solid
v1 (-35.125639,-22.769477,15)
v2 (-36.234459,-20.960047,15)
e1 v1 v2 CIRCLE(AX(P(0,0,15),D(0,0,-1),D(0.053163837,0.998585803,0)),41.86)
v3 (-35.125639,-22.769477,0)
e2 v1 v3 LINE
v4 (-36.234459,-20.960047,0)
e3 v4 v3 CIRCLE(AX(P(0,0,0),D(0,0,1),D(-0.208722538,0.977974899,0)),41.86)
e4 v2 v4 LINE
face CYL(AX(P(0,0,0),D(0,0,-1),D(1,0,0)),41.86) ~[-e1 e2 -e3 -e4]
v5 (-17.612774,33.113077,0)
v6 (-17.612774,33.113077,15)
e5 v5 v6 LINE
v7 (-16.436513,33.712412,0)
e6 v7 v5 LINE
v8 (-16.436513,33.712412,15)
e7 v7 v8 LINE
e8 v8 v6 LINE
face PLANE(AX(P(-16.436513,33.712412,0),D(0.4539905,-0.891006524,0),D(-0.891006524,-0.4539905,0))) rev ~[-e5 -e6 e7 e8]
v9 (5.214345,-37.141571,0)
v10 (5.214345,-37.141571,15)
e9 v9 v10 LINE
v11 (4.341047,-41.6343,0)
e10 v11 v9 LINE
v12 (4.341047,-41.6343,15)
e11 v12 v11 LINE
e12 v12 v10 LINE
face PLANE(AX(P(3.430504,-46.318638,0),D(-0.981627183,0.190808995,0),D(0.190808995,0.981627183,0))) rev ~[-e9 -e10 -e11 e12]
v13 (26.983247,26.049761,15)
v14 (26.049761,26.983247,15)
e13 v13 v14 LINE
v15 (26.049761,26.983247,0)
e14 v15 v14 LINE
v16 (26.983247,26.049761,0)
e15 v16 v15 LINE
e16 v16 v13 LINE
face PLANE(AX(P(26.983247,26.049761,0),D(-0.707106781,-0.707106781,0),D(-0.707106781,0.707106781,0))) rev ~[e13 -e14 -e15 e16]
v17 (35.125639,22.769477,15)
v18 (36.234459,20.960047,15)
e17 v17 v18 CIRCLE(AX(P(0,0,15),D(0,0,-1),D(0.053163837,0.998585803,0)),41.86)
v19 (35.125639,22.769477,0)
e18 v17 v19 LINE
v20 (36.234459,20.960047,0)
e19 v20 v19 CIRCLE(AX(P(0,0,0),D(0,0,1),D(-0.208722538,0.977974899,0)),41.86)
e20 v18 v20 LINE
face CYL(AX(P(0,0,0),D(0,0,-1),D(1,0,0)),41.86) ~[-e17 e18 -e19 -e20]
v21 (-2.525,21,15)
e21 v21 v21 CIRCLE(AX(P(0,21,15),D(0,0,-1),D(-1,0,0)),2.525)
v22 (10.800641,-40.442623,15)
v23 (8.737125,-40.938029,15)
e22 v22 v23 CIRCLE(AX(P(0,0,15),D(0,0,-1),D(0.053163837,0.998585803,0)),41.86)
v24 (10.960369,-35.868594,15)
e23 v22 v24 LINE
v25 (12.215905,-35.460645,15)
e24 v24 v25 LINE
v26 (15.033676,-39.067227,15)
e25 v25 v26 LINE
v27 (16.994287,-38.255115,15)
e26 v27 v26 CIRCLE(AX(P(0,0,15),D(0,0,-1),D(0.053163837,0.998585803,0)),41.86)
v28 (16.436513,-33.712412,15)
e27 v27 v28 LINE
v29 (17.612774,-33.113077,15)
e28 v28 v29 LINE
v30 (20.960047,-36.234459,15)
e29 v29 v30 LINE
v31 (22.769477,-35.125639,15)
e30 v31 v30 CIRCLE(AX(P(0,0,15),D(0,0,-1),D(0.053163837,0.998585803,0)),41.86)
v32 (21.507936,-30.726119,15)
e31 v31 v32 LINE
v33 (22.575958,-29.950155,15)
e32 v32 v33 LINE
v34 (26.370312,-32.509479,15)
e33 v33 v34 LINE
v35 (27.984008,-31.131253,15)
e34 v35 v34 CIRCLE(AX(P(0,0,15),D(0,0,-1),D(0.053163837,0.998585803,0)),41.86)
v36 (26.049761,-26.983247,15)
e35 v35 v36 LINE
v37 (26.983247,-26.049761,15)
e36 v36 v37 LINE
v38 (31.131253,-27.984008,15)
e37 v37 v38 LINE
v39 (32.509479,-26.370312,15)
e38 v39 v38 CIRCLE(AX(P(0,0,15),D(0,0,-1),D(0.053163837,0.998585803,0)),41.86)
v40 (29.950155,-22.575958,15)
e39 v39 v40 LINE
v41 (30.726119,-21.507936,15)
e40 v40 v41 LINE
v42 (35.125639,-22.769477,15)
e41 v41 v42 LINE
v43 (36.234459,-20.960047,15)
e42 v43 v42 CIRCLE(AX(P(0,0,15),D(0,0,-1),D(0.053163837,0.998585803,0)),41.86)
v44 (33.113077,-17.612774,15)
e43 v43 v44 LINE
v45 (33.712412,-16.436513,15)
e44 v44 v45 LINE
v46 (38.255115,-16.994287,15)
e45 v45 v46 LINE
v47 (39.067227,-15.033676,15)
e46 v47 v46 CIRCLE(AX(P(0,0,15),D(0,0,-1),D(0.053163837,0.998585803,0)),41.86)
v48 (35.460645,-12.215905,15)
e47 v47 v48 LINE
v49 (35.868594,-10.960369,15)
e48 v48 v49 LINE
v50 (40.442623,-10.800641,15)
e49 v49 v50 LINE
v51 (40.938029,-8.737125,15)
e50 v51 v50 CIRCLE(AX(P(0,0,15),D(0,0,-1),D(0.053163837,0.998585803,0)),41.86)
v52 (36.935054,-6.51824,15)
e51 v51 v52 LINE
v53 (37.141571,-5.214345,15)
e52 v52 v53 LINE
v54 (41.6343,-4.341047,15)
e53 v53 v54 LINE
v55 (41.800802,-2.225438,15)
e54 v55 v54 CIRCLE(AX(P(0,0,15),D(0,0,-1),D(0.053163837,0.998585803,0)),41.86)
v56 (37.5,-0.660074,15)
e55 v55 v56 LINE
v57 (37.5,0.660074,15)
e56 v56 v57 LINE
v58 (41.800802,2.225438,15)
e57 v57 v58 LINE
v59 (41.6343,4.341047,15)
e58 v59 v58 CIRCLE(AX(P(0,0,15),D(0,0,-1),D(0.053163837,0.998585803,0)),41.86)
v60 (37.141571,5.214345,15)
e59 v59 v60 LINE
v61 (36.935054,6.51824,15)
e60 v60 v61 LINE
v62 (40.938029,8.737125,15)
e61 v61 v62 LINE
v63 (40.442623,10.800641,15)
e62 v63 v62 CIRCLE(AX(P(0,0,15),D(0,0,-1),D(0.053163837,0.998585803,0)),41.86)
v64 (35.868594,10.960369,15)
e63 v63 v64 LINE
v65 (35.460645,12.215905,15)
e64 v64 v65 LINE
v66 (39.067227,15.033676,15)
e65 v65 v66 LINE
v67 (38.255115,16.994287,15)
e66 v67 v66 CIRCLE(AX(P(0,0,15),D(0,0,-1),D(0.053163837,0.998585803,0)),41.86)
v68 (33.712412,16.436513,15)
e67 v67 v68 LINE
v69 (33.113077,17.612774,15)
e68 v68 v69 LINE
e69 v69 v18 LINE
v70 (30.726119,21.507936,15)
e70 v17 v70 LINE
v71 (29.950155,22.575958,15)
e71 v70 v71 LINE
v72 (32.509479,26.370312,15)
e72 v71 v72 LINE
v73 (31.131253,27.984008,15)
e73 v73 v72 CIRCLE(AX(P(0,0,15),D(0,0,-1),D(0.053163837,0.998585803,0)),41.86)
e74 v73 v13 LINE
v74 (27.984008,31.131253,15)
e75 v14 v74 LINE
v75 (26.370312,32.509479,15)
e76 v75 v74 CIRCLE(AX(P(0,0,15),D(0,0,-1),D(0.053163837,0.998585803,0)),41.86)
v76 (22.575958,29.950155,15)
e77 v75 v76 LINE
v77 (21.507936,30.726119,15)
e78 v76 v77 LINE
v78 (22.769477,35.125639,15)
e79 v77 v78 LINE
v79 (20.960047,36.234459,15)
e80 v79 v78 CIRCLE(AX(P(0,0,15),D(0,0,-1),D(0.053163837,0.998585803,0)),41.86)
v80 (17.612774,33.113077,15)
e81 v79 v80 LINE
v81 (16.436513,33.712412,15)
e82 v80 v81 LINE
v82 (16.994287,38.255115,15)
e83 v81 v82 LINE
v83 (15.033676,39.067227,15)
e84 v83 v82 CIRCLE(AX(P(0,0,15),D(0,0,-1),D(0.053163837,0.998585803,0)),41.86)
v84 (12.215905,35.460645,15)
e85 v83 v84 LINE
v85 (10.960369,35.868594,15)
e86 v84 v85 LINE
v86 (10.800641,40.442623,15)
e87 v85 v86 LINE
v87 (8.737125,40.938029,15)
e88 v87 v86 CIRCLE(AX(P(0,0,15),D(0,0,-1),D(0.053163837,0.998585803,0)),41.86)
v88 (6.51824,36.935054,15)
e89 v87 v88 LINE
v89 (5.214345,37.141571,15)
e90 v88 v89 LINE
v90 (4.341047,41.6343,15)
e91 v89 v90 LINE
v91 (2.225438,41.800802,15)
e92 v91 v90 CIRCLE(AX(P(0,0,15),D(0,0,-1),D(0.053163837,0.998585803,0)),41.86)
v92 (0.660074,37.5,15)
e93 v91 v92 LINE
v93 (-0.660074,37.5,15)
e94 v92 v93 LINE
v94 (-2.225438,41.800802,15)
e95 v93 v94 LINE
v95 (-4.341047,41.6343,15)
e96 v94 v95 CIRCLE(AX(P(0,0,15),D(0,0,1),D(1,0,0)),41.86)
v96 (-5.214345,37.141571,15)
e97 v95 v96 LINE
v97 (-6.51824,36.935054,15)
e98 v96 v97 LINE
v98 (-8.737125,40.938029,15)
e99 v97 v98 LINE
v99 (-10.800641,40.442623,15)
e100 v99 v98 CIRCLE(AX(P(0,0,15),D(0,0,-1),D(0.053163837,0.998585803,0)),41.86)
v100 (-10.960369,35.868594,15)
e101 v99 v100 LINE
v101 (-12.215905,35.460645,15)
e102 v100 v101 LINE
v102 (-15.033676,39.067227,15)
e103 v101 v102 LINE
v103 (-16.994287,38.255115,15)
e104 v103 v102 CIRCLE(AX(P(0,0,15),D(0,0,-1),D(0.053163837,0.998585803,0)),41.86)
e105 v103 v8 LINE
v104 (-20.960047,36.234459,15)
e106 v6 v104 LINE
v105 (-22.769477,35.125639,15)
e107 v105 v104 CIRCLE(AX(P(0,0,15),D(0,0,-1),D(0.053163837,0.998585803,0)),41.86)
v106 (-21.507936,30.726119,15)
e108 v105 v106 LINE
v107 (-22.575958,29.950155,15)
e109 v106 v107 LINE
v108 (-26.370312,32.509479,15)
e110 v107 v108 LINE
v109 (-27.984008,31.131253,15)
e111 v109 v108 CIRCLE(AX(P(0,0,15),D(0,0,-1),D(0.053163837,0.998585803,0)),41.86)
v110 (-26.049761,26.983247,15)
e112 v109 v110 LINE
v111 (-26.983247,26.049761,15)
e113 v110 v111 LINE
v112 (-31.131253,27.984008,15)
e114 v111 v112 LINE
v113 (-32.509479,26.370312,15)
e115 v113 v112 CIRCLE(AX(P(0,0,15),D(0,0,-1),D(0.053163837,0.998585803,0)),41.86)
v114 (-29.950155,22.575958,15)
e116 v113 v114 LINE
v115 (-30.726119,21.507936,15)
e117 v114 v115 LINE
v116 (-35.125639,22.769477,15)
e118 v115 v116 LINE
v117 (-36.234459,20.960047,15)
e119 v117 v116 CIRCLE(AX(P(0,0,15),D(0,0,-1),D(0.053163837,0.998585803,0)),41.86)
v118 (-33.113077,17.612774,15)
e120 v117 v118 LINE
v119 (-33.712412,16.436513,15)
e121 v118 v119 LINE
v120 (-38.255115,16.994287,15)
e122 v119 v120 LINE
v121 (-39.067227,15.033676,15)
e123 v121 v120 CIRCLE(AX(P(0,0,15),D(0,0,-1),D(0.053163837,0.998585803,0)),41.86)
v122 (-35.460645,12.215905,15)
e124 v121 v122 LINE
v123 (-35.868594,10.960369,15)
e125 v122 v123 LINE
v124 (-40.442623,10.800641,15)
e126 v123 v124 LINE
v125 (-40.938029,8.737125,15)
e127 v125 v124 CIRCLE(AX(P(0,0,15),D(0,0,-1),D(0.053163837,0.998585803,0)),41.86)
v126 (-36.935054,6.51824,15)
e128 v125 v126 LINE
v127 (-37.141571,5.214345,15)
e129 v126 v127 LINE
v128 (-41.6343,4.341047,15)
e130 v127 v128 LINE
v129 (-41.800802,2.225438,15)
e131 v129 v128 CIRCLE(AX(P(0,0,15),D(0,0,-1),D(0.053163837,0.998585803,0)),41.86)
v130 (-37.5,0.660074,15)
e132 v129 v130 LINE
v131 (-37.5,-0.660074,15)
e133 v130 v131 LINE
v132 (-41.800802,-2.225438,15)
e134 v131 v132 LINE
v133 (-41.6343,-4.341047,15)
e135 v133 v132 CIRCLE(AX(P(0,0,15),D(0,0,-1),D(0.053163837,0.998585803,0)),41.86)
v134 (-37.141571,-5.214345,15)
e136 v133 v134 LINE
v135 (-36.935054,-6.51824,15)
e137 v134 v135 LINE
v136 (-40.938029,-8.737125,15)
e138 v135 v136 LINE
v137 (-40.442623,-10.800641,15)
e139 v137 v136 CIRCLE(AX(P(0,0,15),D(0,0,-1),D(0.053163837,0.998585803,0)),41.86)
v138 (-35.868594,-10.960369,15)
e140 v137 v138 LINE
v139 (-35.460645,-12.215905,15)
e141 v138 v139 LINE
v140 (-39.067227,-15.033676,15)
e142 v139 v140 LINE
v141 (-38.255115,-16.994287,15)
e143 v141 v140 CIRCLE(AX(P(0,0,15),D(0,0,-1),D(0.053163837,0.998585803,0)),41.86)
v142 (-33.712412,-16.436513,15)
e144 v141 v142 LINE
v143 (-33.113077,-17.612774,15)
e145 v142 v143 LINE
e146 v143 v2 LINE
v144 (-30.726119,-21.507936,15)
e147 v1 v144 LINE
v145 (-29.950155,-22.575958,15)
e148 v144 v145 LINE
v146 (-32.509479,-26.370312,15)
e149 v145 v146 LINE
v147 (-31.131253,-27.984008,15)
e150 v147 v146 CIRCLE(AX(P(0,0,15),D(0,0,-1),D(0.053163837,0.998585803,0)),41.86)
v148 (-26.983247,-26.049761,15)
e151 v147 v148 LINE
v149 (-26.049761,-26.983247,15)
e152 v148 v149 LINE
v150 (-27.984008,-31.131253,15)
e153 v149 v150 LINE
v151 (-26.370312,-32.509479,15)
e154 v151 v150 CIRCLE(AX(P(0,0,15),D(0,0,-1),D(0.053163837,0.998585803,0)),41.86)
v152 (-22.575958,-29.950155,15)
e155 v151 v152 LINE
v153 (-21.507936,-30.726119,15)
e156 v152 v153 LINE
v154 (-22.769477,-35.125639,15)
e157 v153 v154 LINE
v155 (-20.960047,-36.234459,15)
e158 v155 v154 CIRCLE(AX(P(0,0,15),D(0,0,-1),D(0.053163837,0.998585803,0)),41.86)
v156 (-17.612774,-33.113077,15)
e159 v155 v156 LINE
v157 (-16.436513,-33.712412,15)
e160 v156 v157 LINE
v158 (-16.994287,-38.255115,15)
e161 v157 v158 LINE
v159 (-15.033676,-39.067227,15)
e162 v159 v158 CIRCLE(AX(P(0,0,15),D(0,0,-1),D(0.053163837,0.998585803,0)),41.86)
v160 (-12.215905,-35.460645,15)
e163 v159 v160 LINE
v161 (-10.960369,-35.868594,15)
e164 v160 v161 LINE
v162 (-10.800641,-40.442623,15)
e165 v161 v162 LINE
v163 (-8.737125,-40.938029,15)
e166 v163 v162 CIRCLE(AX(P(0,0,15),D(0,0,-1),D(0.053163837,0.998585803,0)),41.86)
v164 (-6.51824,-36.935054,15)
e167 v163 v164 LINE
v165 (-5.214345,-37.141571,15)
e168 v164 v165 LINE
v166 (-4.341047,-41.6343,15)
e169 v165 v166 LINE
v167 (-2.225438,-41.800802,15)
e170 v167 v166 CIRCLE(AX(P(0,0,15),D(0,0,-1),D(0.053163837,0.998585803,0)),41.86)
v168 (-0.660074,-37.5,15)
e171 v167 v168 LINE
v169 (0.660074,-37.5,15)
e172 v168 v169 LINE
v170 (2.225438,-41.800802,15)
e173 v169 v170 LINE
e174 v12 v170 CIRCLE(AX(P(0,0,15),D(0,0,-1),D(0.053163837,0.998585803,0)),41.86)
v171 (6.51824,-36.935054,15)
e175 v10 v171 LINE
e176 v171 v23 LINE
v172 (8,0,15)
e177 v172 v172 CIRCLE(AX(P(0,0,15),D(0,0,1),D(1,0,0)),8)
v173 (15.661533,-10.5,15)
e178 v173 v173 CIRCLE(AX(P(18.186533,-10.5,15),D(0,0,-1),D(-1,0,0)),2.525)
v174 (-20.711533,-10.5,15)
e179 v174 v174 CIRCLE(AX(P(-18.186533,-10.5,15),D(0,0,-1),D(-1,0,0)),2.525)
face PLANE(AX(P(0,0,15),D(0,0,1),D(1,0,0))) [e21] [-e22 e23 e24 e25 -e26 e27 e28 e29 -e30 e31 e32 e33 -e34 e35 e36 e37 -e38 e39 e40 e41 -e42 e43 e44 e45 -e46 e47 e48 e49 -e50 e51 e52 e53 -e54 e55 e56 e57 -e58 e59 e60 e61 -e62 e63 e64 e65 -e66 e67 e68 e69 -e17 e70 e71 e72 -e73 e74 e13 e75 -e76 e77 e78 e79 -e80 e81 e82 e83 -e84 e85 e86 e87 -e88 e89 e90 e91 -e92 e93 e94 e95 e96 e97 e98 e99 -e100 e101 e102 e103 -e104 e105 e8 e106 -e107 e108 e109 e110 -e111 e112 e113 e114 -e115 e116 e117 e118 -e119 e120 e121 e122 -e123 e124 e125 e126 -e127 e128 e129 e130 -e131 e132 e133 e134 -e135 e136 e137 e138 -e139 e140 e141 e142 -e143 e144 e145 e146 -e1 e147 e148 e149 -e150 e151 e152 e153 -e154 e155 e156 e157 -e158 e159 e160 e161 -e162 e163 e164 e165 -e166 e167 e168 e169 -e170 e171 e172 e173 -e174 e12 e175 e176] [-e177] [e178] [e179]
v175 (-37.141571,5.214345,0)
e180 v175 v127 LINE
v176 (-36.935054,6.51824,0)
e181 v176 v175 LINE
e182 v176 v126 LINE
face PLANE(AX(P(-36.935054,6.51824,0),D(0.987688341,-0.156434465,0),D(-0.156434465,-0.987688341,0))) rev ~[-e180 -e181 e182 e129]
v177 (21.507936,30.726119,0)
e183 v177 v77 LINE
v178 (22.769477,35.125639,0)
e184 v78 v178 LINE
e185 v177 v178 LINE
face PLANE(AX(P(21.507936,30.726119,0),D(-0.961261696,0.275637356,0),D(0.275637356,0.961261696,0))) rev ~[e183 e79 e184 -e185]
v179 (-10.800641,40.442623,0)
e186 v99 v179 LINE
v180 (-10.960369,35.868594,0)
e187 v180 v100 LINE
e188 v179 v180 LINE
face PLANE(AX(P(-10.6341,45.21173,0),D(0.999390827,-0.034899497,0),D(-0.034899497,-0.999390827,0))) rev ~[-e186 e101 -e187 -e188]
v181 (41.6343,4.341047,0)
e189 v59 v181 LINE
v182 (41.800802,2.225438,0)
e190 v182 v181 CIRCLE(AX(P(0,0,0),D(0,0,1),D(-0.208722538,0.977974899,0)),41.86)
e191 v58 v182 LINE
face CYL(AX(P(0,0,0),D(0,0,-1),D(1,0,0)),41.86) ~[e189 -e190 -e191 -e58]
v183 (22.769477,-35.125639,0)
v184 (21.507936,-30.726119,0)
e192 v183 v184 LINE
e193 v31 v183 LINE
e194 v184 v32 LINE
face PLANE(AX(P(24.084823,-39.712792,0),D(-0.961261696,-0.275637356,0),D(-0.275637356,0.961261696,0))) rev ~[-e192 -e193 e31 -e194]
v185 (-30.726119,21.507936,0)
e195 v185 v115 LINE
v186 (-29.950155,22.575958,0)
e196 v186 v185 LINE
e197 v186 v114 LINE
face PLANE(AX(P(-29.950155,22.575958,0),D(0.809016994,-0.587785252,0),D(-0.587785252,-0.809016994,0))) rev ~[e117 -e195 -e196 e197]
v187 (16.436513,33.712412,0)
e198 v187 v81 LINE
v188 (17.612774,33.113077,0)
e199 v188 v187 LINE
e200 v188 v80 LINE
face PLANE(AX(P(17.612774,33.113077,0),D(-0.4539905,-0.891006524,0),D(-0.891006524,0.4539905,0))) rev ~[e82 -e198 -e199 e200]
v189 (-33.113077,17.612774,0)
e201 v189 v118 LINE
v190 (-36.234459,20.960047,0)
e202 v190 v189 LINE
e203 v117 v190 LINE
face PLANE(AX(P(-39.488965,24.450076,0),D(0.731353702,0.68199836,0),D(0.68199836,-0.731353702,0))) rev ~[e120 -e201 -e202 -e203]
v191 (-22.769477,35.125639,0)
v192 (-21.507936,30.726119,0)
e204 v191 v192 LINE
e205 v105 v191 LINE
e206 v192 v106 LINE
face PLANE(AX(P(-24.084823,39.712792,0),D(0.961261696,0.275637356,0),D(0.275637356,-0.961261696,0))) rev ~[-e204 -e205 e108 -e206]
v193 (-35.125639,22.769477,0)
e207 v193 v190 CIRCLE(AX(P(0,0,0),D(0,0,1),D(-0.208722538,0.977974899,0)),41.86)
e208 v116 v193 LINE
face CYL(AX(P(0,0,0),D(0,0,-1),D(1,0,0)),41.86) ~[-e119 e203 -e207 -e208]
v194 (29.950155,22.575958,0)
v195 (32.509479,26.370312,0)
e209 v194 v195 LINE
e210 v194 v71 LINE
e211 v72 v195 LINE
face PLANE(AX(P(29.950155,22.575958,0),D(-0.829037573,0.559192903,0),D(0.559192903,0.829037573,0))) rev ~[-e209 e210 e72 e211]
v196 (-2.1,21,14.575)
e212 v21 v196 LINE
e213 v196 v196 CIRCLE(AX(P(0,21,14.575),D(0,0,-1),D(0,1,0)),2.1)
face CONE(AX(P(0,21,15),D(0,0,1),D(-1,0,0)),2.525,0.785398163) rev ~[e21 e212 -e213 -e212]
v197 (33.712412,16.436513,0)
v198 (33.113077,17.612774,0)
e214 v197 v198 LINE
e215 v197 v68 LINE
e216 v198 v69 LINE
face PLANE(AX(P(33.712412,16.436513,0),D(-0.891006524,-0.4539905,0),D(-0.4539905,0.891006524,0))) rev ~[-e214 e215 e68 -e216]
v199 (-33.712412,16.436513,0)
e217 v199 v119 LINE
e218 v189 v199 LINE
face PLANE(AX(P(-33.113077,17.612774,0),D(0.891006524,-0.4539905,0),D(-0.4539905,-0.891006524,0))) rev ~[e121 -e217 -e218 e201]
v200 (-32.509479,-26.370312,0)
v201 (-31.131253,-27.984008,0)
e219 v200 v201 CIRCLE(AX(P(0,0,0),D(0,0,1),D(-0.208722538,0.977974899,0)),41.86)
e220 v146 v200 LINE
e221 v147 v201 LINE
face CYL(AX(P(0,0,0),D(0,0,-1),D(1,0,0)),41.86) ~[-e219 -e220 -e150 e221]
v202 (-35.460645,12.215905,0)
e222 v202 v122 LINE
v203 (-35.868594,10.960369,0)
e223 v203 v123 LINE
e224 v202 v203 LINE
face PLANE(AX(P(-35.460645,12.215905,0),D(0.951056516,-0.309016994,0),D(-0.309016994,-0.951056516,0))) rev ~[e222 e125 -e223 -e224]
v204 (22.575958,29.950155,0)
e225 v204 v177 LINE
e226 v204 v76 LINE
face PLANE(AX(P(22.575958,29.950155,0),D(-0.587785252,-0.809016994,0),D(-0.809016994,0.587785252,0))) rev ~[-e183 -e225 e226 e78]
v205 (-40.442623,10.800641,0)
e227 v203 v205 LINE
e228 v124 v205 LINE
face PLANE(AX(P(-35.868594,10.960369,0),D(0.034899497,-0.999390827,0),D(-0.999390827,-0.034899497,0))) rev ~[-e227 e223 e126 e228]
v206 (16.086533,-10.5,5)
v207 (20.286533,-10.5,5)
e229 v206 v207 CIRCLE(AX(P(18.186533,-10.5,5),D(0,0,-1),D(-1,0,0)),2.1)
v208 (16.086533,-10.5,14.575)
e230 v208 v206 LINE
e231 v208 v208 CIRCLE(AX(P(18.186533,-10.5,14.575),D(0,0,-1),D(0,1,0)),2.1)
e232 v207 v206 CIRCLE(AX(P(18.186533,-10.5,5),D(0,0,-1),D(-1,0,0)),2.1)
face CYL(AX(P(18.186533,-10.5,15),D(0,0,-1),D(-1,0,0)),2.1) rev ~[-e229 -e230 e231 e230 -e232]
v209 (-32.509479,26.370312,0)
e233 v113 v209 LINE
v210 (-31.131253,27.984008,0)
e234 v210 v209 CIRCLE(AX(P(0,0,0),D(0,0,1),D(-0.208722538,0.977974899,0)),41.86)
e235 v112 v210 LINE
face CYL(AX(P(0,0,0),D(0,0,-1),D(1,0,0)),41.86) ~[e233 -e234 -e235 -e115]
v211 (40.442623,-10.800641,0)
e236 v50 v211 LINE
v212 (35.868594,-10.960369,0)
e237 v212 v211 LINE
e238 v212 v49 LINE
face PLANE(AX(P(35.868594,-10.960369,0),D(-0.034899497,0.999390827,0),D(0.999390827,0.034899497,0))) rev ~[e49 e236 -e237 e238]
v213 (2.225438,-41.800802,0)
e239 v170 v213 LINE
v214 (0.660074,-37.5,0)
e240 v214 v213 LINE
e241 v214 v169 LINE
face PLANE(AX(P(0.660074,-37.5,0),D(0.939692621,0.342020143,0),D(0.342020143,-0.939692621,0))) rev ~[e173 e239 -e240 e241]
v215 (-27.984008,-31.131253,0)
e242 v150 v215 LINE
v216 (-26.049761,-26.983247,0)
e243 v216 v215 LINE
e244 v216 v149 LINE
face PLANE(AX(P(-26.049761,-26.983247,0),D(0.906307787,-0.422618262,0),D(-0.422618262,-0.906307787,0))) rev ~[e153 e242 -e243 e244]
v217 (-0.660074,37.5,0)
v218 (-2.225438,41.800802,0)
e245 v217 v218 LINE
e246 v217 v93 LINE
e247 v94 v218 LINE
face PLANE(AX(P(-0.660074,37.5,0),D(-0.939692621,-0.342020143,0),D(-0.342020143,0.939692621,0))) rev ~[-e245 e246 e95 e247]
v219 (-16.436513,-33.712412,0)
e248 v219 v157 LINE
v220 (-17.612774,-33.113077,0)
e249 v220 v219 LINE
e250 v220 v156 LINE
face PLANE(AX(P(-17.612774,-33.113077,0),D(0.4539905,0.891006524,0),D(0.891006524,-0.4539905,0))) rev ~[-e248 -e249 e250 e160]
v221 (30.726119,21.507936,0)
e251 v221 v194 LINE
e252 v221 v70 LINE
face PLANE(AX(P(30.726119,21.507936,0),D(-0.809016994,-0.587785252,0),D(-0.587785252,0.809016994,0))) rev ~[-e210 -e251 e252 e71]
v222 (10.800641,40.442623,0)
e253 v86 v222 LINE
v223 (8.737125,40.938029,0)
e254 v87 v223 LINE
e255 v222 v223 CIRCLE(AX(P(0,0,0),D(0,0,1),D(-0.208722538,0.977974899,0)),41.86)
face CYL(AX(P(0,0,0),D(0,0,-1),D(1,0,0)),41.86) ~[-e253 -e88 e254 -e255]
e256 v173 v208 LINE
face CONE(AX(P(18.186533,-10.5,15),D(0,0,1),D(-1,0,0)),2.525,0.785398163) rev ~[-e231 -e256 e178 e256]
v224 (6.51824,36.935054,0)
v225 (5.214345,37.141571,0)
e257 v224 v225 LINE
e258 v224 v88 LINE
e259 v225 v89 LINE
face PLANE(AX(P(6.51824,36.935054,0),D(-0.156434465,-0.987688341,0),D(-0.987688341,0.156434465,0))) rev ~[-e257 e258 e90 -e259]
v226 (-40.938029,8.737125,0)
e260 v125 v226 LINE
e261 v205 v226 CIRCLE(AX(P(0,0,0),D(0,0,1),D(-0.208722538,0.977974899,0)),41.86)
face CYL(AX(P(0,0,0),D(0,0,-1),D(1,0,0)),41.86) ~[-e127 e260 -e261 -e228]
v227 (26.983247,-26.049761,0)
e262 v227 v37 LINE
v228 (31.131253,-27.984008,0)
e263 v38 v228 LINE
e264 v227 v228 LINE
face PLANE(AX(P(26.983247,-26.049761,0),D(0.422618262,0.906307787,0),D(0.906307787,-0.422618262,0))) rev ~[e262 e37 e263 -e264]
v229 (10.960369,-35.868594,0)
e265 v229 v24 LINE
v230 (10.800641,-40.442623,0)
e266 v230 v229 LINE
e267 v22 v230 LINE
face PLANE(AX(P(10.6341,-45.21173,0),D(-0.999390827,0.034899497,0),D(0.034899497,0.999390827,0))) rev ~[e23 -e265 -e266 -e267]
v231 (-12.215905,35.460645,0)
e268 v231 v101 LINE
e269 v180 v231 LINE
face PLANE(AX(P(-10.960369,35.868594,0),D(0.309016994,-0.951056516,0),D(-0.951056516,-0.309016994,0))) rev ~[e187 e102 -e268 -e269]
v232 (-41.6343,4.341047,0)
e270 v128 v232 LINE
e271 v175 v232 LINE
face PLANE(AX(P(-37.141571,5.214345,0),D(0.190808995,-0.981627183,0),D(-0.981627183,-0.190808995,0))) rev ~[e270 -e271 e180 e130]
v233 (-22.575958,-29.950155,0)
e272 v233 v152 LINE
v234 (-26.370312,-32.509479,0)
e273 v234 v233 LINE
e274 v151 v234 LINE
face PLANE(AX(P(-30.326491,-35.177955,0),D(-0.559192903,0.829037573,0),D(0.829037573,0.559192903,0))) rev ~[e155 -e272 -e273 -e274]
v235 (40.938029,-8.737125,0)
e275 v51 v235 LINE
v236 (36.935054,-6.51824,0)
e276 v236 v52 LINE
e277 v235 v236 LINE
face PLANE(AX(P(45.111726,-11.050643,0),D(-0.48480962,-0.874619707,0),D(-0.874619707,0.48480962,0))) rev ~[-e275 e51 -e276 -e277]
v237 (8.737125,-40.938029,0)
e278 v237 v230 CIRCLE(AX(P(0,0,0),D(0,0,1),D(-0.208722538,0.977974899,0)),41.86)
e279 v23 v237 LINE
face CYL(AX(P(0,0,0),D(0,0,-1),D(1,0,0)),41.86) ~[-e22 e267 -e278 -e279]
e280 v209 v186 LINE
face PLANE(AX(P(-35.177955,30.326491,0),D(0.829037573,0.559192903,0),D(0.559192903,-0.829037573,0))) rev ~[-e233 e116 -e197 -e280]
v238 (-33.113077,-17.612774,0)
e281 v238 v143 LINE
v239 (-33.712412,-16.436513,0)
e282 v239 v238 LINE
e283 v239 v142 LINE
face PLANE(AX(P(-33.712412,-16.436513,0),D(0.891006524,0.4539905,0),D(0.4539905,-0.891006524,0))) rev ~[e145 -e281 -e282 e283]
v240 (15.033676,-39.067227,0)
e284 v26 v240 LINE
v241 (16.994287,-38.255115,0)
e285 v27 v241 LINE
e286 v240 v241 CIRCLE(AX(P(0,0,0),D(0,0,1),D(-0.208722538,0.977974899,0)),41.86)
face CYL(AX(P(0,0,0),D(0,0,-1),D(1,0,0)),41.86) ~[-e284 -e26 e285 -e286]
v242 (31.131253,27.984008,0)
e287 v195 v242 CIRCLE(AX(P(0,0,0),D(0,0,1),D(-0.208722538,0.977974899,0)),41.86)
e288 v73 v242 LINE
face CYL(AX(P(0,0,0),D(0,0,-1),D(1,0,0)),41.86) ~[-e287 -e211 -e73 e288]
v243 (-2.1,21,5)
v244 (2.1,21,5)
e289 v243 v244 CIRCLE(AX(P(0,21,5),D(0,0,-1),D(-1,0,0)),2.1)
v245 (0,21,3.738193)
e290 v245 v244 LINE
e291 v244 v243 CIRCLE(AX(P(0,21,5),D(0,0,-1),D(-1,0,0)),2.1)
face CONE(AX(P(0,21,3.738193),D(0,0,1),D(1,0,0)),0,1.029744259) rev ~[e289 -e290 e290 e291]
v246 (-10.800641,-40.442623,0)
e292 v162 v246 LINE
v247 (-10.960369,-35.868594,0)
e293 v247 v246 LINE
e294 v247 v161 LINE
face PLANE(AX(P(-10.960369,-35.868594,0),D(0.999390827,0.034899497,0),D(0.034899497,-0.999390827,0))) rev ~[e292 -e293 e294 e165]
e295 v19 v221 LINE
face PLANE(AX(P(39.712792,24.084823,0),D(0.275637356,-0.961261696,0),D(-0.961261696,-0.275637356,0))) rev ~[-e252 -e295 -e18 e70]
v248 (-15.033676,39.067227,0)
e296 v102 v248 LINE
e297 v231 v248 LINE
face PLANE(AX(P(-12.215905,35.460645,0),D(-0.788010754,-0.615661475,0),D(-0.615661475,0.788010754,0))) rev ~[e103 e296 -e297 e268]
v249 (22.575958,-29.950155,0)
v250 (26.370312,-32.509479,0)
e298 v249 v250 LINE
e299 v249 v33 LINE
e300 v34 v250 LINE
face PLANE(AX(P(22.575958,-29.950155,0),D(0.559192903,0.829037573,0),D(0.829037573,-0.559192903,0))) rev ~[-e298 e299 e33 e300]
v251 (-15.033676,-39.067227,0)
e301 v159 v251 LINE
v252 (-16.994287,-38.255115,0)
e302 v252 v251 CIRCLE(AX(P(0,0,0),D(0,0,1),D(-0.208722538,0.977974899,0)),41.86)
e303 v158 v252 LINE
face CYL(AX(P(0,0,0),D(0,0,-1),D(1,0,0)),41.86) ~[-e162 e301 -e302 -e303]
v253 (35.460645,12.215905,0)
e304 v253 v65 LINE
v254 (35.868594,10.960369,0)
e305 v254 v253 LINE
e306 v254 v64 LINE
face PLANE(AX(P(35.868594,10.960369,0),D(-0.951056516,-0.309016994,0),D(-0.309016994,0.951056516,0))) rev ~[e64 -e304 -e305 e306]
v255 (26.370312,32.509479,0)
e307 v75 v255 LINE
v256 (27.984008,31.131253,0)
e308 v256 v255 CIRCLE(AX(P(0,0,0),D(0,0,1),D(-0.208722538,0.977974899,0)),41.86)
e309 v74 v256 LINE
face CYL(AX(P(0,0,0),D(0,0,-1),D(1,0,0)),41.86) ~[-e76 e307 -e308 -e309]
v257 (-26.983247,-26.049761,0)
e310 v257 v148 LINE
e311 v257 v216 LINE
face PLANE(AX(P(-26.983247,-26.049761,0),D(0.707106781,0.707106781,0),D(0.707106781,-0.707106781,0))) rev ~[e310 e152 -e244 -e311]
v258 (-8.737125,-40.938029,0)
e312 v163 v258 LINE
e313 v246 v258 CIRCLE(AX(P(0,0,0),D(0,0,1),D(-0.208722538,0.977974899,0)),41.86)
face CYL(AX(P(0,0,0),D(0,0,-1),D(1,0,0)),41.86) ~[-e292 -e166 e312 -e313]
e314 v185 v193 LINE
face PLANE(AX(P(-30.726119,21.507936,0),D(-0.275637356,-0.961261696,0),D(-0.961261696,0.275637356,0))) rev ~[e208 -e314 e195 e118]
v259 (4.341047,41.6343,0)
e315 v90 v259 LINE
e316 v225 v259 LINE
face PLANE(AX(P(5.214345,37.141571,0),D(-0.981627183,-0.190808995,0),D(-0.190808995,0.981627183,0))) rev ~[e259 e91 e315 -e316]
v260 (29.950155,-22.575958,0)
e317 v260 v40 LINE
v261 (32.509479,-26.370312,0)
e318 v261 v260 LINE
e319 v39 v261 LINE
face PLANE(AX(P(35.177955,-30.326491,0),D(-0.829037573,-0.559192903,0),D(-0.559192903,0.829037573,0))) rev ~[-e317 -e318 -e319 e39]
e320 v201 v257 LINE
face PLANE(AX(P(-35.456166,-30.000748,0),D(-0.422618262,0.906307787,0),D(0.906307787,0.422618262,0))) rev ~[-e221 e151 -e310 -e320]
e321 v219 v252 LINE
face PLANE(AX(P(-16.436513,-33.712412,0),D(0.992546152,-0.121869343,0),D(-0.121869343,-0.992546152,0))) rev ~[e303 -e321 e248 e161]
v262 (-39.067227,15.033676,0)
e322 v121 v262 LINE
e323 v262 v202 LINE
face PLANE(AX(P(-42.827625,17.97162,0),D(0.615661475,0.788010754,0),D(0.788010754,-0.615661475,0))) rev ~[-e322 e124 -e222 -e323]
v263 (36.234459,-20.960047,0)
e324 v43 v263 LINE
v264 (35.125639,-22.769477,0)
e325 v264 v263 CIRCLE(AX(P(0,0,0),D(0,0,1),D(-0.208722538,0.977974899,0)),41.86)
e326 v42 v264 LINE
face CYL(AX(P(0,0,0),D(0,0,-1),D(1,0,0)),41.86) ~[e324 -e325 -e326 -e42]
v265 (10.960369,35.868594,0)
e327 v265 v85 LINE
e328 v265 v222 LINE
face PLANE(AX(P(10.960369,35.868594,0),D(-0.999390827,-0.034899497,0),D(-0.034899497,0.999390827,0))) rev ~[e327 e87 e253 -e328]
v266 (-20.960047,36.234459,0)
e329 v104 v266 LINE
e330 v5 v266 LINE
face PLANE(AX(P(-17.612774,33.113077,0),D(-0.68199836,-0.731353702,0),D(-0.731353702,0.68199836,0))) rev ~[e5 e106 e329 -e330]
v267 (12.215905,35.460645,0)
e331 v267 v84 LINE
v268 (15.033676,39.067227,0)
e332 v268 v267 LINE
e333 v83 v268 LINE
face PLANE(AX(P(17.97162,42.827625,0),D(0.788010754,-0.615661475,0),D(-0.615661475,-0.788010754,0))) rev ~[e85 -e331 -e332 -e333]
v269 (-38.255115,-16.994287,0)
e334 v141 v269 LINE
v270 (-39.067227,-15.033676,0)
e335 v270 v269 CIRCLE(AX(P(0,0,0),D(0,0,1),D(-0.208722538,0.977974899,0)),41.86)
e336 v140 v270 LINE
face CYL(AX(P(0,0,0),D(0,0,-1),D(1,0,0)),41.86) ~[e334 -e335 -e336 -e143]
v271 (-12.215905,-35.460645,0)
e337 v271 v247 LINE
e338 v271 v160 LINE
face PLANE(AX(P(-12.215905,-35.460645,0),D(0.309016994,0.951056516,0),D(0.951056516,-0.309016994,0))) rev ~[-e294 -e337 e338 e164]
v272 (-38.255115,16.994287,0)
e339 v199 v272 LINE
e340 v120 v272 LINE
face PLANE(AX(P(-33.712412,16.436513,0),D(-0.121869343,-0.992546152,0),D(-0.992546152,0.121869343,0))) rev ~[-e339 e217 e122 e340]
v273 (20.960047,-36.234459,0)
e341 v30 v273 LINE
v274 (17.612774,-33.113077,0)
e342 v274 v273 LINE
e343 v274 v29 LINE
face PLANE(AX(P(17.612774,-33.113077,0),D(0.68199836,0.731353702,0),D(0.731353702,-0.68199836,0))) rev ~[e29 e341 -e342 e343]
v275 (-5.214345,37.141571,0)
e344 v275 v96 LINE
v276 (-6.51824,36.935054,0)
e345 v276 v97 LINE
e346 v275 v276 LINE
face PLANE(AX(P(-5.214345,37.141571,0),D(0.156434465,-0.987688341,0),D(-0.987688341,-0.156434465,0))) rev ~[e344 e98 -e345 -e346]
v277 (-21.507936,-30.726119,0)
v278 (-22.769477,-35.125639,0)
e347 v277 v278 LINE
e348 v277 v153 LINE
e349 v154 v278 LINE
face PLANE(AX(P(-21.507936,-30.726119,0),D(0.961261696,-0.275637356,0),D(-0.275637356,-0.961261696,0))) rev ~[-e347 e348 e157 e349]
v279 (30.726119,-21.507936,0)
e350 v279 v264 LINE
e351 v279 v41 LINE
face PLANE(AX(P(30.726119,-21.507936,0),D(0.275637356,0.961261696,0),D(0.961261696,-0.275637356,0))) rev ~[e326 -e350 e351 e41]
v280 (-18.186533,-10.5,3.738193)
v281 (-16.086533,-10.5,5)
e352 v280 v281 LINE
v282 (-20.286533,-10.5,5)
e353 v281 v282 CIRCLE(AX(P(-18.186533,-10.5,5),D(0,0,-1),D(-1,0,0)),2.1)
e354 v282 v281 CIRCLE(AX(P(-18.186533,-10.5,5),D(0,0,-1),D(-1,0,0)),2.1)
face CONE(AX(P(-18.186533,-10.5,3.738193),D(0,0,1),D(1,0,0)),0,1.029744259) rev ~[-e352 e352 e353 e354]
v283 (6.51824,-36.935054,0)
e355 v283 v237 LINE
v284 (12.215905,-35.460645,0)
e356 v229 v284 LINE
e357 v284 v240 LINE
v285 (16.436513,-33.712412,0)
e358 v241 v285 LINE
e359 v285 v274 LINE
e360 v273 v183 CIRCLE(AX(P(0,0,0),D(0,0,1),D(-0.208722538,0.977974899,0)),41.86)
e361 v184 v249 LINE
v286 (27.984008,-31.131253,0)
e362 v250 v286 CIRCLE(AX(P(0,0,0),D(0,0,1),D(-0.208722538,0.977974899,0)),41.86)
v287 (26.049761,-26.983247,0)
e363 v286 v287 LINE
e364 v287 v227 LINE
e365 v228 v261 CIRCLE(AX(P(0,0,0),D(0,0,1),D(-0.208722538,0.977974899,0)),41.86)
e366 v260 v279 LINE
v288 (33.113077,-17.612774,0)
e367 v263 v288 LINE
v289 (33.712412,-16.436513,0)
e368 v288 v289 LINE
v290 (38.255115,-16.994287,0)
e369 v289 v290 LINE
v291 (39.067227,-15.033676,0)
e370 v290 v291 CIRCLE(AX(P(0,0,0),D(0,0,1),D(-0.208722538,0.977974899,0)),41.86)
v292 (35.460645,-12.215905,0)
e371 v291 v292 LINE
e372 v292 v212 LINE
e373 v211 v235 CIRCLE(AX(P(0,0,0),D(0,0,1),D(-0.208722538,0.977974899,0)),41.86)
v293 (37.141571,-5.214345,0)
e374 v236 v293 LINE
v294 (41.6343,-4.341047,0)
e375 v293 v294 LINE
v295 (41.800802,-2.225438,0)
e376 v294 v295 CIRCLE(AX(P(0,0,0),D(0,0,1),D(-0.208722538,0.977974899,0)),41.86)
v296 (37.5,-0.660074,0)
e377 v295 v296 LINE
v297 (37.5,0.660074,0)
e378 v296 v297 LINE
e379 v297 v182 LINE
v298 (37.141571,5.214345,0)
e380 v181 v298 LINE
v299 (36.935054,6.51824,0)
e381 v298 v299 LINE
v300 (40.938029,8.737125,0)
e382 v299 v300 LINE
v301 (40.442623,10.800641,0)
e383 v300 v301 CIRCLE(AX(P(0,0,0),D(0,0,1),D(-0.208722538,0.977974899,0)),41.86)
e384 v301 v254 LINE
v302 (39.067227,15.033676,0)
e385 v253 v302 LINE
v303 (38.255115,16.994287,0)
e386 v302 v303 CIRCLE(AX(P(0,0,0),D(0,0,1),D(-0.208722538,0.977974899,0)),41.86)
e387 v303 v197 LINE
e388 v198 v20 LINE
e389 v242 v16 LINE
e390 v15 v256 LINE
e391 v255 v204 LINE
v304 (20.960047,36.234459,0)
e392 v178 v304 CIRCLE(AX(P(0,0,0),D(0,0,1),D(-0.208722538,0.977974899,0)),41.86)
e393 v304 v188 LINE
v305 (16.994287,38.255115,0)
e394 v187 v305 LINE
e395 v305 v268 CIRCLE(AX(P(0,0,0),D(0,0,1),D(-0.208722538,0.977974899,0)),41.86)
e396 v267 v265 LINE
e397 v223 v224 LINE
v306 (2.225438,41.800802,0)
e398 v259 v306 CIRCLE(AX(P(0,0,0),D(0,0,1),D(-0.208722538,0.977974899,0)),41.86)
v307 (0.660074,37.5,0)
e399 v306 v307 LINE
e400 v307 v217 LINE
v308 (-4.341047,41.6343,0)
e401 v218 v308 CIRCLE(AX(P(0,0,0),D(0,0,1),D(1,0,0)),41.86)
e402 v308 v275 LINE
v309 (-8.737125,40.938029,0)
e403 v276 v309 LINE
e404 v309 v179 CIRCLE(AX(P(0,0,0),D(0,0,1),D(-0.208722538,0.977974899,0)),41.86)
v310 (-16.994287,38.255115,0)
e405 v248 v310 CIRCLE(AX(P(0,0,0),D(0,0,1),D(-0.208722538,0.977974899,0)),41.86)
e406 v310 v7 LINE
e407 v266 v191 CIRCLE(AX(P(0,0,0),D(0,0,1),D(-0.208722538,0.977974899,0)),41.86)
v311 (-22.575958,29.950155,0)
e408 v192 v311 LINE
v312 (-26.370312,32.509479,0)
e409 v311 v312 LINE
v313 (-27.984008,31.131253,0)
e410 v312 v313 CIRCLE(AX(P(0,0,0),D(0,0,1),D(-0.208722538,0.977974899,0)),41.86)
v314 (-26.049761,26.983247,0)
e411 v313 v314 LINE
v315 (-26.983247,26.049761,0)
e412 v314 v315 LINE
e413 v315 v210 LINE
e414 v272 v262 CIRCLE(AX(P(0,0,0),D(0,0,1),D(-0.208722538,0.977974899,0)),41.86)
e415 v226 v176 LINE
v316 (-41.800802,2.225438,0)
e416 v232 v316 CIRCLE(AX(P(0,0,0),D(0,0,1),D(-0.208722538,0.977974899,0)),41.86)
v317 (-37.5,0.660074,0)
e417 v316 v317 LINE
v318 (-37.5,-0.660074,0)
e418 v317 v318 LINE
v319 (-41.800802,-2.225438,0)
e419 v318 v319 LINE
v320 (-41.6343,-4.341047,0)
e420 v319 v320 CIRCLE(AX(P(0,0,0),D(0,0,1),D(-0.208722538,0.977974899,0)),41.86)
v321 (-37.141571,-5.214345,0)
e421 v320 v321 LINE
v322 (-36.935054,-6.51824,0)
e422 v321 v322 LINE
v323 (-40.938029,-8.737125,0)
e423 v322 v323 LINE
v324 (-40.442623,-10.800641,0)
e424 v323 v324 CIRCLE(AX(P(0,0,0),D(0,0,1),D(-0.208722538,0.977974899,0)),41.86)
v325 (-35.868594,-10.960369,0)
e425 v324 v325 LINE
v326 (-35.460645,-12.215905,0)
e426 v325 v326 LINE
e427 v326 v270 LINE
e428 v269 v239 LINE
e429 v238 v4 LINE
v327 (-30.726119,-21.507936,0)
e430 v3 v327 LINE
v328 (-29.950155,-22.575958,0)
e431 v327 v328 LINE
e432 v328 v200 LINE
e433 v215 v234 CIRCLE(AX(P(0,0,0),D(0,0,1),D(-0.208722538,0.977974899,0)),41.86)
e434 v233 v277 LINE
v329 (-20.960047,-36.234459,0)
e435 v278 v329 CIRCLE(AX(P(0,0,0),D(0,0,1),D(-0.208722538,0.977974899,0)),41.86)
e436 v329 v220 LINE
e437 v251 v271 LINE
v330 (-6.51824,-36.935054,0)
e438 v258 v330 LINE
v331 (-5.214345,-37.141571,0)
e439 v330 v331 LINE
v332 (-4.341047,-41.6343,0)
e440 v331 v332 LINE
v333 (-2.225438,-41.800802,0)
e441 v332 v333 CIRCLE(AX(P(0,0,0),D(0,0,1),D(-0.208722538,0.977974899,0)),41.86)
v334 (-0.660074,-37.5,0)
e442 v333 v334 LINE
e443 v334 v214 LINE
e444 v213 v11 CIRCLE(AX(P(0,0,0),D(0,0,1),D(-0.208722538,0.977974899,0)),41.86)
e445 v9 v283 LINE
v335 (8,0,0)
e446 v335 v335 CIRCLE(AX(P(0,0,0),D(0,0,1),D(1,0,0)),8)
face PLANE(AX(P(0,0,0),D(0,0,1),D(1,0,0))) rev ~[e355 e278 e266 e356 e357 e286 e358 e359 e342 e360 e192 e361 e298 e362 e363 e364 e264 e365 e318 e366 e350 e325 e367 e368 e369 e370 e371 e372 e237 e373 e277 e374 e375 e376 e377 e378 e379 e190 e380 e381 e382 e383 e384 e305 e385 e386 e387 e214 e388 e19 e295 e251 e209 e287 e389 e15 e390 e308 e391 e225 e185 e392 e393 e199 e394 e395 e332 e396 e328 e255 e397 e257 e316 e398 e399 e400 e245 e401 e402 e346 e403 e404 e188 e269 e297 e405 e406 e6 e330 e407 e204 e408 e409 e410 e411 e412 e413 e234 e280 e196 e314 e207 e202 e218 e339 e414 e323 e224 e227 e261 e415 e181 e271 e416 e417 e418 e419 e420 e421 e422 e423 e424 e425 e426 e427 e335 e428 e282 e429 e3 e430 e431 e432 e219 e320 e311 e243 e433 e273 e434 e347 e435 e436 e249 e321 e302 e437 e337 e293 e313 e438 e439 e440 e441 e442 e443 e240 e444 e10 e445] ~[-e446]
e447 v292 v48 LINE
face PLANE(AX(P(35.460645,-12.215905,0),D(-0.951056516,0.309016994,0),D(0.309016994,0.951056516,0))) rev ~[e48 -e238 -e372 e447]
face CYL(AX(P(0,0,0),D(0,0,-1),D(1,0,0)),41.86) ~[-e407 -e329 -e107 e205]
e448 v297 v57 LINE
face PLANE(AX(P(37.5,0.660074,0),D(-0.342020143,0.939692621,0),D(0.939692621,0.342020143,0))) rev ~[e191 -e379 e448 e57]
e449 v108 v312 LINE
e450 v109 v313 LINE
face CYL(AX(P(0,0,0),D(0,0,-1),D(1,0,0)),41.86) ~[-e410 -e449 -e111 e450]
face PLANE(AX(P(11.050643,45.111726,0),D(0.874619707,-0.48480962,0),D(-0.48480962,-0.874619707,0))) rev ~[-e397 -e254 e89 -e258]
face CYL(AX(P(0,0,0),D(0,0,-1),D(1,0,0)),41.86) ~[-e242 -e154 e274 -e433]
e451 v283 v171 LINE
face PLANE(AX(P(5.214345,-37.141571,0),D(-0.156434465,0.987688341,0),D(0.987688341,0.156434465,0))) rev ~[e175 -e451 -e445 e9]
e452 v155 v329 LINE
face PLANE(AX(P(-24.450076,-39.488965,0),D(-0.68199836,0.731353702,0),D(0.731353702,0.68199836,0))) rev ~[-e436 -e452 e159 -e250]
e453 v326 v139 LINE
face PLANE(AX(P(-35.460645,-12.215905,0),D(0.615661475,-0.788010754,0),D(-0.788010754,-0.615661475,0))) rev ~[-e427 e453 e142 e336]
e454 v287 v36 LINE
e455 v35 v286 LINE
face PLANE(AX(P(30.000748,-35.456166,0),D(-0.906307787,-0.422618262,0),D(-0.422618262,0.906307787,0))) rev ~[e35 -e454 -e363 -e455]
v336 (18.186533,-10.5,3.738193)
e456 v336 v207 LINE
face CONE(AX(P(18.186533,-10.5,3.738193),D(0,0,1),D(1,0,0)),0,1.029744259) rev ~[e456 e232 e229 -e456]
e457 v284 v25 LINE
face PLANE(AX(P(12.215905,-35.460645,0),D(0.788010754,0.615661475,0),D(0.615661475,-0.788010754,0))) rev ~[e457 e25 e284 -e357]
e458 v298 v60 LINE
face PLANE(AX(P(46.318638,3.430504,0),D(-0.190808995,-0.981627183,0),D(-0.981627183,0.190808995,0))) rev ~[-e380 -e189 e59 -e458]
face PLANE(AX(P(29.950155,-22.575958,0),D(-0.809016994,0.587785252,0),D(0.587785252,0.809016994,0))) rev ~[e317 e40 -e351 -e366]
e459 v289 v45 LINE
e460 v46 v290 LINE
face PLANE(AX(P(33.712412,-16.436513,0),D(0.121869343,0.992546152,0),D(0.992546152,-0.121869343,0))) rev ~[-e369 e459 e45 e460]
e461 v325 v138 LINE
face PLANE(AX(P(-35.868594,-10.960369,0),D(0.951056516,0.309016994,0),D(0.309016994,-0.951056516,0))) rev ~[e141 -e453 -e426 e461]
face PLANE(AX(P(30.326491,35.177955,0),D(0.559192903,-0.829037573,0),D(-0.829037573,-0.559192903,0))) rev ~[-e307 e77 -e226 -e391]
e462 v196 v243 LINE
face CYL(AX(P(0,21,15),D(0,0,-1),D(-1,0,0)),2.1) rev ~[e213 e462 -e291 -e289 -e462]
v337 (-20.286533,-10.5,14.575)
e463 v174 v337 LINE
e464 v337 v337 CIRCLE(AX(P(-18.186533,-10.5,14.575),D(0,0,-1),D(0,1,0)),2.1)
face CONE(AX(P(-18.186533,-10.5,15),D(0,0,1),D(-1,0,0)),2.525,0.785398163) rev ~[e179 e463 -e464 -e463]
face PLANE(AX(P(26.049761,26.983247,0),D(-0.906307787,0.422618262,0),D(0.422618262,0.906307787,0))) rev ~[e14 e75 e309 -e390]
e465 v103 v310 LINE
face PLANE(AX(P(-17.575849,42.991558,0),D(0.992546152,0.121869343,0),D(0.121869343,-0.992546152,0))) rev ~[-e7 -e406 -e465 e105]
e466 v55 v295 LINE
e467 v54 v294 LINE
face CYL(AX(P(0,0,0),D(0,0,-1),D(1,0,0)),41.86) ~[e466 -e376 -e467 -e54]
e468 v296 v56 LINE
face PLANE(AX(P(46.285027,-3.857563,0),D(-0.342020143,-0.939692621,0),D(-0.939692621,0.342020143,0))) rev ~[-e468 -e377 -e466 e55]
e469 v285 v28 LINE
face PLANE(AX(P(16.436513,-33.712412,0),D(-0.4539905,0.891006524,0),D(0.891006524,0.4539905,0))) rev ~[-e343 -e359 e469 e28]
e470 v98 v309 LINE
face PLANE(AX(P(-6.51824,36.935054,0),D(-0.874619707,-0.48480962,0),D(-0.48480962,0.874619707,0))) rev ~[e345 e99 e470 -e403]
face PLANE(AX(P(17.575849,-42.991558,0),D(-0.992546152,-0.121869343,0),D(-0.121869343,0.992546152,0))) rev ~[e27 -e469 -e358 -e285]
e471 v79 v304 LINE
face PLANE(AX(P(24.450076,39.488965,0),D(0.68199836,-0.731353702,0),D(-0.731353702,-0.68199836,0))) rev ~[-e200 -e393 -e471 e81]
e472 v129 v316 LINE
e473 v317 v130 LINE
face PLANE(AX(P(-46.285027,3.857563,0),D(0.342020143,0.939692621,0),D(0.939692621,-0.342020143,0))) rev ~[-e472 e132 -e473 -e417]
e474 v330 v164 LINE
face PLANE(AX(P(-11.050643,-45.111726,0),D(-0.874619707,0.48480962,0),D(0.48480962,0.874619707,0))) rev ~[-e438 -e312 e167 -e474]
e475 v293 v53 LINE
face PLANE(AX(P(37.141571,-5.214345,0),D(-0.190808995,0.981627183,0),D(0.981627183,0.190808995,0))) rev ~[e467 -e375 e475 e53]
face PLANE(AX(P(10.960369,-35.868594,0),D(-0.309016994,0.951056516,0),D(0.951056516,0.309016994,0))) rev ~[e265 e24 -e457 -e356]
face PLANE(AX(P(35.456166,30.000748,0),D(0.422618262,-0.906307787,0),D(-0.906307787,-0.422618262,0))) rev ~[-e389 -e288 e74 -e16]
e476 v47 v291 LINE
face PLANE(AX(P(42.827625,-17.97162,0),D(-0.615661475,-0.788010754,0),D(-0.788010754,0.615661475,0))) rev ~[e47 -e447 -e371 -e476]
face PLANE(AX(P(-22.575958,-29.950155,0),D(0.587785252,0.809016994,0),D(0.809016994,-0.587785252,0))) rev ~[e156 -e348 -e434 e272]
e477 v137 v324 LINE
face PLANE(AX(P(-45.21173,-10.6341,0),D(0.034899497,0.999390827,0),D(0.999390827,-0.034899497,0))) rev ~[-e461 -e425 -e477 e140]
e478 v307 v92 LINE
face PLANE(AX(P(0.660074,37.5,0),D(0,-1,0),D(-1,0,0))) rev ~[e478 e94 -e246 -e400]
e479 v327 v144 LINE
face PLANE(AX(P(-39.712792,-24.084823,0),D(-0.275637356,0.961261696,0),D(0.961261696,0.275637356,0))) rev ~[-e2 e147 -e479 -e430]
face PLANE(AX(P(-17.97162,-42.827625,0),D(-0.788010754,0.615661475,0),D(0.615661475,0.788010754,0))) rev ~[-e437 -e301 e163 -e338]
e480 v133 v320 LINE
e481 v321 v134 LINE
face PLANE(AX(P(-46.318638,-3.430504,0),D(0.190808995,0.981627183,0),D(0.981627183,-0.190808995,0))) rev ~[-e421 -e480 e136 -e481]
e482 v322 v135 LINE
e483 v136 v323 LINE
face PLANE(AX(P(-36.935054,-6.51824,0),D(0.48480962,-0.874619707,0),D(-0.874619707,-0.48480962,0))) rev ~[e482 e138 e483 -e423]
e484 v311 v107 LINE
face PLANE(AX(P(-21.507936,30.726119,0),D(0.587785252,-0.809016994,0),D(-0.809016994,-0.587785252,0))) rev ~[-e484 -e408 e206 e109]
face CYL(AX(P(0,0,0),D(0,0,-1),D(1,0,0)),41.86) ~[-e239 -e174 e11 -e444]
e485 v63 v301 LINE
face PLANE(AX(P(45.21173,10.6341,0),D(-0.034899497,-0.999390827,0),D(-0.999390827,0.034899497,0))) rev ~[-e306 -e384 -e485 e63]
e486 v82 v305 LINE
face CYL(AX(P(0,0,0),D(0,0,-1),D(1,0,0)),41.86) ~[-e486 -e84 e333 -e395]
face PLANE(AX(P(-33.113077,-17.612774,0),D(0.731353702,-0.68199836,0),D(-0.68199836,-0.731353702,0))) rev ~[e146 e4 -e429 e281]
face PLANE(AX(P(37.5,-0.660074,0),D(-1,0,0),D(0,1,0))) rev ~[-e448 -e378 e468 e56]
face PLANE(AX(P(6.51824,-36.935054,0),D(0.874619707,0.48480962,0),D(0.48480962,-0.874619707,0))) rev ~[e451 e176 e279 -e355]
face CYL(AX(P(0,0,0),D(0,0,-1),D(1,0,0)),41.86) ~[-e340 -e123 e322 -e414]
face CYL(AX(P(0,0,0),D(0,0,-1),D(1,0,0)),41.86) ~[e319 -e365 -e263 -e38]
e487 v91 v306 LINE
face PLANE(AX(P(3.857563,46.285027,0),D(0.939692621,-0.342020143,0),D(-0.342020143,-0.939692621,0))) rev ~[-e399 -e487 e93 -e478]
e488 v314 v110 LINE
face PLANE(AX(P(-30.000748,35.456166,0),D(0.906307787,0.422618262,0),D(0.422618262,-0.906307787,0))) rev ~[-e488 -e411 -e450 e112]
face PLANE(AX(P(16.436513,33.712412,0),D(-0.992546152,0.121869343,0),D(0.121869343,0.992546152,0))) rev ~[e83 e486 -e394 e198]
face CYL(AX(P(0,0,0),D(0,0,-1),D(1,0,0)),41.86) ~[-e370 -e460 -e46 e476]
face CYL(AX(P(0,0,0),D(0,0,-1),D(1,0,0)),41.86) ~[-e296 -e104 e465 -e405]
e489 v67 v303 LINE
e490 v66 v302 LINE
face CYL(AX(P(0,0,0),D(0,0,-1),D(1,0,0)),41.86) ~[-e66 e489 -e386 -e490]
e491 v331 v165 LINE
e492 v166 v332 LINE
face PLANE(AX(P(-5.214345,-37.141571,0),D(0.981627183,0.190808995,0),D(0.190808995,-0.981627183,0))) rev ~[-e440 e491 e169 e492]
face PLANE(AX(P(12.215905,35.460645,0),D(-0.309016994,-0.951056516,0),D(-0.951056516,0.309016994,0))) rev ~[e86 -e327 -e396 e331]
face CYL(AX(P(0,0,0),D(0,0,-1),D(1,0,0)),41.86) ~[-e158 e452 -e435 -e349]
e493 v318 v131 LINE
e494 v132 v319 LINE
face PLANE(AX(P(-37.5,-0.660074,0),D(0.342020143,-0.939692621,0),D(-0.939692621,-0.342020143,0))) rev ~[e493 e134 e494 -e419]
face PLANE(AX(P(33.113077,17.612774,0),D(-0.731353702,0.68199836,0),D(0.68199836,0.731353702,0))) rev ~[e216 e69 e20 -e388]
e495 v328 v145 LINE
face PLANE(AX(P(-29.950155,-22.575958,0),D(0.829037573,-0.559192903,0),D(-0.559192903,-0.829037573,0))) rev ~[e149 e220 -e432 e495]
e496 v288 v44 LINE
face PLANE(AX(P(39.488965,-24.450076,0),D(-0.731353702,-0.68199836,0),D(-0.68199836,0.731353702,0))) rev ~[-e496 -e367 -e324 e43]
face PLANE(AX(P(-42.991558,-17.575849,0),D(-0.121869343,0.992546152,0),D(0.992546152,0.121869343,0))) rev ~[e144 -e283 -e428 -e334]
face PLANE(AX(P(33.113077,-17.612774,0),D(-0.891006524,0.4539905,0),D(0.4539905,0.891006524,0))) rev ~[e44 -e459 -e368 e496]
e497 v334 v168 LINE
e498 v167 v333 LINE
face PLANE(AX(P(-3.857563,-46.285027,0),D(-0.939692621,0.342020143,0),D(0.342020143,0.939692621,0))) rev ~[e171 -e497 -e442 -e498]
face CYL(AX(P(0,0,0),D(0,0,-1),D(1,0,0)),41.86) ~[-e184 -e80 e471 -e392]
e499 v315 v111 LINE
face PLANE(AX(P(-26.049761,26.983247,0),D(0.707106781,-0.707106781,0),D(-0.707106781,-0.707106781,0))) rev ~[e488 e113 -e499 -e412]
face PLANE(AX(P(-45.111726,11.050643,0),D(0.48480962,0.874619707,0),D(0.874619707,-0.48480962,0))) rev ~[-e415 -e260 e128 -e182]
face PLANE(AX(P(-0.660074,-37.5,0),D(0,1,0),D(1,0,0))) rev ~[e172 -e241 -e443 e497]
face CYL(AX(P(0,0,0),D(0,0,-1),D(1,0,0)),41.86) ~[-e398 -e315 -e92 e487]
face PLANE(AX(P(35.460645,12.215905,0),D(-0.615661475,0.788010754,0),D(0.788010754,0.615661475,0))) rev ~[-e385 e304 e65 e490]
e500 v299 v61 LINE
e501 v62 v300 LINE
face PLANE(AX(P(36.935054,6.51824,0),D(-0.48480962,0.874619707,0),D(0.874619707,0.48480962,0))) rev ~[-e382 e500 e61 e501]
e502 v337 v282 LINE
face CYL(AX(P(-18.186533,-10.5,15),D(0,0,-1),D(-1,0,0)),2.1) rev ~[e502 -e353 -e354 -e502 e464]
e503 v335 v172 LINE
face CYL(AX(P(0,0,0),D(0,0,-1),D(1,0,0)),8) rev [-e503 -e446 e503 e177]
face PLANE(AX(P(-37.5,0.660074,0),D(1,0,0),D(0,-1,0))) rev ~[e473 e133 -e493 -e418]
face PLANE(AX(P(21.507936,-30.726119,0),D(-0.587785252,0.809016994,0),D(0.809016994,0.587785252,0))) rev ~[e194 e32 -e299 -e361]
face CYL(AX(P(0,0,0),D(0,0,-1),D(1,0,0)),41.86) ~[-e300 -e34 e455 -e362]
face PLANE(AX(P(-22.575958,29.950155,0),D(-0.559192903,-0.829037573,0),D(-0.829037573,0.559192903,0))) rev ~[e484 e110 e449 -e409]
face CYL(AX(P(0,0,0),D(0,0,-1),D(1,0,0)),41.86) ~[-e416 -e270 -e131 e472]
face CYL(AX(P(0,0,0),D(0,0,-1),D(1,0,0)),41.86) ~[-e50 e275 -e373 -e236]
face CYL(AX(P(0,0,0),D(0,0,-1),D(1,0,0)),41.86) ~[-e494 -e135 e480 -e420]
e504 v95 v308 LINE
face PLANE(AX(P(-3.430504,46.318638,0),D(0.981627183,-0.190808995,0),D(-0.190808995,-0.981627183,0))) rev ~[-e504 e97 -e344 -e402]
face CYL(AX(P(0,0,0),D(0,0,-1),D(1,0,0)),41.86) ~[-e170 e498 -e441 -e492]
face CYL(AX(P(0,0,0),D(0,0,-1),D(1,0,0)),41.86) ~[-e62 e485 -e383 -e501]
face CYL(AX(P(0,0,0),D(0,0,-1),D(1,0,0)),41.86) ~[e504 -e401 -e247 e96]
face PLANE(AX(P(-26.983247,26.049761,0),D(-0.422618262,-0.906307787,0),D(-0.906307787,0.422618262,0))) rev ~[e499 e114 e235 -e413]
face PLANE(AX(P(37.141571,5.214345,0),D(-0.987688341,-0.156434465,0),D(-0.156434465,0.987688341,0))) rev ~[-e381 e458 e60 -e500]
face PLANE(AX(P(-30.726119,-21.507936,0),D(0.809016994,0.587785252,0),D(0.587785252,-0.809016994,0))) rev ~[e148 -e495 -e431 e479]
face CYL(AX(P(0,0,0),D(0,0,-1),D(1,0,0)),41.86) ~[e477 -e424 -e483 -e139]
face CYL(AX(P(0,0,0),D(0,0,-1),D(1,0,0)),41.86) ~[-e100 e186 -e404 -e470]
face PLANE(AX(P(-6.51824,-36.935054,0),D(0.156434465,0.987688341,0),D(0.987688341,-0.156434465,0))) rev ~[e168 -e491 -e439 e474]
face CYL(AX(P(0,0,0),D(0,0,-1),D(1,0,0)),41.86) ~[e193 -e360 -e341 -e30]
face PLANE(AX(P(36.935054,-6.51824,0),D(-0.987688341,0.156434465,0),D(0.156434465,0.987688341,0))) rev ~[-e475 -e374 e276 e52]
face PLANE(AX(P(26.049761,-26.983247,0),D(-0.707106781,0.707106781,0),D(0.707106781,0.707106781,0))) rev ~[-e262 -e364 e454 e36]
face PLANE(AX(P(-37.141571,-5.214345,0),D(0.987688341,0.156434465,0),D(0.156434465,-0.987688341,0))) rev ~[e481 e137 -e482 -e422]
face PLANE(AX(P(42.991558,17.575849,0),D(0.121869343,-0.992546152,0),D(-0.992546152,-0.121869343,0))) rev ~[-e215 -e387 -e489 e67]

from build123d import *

# Parameters (mm, degrees)
SKETCH1_R                   = 41.86
SKETCH1_R_2                 = 8
BOSS_EXTRUDE1_DEPTH         = 15
M5_TAPPED_HOLE1_D           = 4.2
M5_TAPPED_HOLE1_DEPTH       = 10
M5_TAPPED_HOLE1_CSINK_D     = 5.05
M5_TAPPED_HOLE1_CSINK_ANGLE = 90
M5_TAPPED_HOLE1_TIP         = 1.2618073
CUT_EXTRUDE1_DEPTH          = 15
CIRPATTERN1_COUNT           = 40


with BuildPart() as part:
    # Sketch1 → Boss-Extrude1 (new body)
    with BuildSketch(Plane.XY):
        Circle(SKETCH1_R)
        Circle(SKETCH1_R_2, mode=Mode.SUBTRACT)
    extrude(amount=BOSS_EXTRUDE1_DEPTH)

    # M5 Tapped Hole1
    with Locations(Plane.XY.offset(15)):
        with Locations((-18.186533479, -10.5), (0, 21), (18.186533479, -10.5)):
            CounterSinkHole(M5_TAPPED_HOLE1_D / 2, M5_TAPPED_HOLE1_CSINK_D / 2, depth=M5_TAPPED_HOLE1_DEPTH, counter_sink_angle=M5_TAPPED_HOLE1_CSINK_ANGLE)
            with Locations((0, 0, -(M5_TAPPED_HOLE1_DEPTH + M5_TAPPED_HOLE1_TIP / 2))):  # 118° drill point
                Cone(0, M5_TAPPED_HOLE1_D / 2, M5_TAPPED_HOLE1_TIP, mode=Mode.SUBTRACT)

    # Sketch4 → Cut-Extrude1 (cut)
    with BuildSketch(Plane.XY):
        Polygon((0.660074414, 37.5), (-0.660074414, 37.5), (-3.857562929, 46.285027494), (3.857562929, 46.285027494), align=None)
    cut_extrude1 = extrude(amount=CUT_EXTRUDE1_DEPTH, mode=Mode.SUBTRACT)

    # CirPattern1: Cut-Extrude1 ×40 about axis
    cirpattern1_axis = Axis((0, 0, 0), (0, 0, 1))
    for i in range(1, CIRPATTERN1_COUNT):
        add(cut_extrude1.rotate(cirpattern1_axis, i * 360 / CIRPATTERN1_COUNT), mode=Mode.SUBTRACT)


solid = part.part
